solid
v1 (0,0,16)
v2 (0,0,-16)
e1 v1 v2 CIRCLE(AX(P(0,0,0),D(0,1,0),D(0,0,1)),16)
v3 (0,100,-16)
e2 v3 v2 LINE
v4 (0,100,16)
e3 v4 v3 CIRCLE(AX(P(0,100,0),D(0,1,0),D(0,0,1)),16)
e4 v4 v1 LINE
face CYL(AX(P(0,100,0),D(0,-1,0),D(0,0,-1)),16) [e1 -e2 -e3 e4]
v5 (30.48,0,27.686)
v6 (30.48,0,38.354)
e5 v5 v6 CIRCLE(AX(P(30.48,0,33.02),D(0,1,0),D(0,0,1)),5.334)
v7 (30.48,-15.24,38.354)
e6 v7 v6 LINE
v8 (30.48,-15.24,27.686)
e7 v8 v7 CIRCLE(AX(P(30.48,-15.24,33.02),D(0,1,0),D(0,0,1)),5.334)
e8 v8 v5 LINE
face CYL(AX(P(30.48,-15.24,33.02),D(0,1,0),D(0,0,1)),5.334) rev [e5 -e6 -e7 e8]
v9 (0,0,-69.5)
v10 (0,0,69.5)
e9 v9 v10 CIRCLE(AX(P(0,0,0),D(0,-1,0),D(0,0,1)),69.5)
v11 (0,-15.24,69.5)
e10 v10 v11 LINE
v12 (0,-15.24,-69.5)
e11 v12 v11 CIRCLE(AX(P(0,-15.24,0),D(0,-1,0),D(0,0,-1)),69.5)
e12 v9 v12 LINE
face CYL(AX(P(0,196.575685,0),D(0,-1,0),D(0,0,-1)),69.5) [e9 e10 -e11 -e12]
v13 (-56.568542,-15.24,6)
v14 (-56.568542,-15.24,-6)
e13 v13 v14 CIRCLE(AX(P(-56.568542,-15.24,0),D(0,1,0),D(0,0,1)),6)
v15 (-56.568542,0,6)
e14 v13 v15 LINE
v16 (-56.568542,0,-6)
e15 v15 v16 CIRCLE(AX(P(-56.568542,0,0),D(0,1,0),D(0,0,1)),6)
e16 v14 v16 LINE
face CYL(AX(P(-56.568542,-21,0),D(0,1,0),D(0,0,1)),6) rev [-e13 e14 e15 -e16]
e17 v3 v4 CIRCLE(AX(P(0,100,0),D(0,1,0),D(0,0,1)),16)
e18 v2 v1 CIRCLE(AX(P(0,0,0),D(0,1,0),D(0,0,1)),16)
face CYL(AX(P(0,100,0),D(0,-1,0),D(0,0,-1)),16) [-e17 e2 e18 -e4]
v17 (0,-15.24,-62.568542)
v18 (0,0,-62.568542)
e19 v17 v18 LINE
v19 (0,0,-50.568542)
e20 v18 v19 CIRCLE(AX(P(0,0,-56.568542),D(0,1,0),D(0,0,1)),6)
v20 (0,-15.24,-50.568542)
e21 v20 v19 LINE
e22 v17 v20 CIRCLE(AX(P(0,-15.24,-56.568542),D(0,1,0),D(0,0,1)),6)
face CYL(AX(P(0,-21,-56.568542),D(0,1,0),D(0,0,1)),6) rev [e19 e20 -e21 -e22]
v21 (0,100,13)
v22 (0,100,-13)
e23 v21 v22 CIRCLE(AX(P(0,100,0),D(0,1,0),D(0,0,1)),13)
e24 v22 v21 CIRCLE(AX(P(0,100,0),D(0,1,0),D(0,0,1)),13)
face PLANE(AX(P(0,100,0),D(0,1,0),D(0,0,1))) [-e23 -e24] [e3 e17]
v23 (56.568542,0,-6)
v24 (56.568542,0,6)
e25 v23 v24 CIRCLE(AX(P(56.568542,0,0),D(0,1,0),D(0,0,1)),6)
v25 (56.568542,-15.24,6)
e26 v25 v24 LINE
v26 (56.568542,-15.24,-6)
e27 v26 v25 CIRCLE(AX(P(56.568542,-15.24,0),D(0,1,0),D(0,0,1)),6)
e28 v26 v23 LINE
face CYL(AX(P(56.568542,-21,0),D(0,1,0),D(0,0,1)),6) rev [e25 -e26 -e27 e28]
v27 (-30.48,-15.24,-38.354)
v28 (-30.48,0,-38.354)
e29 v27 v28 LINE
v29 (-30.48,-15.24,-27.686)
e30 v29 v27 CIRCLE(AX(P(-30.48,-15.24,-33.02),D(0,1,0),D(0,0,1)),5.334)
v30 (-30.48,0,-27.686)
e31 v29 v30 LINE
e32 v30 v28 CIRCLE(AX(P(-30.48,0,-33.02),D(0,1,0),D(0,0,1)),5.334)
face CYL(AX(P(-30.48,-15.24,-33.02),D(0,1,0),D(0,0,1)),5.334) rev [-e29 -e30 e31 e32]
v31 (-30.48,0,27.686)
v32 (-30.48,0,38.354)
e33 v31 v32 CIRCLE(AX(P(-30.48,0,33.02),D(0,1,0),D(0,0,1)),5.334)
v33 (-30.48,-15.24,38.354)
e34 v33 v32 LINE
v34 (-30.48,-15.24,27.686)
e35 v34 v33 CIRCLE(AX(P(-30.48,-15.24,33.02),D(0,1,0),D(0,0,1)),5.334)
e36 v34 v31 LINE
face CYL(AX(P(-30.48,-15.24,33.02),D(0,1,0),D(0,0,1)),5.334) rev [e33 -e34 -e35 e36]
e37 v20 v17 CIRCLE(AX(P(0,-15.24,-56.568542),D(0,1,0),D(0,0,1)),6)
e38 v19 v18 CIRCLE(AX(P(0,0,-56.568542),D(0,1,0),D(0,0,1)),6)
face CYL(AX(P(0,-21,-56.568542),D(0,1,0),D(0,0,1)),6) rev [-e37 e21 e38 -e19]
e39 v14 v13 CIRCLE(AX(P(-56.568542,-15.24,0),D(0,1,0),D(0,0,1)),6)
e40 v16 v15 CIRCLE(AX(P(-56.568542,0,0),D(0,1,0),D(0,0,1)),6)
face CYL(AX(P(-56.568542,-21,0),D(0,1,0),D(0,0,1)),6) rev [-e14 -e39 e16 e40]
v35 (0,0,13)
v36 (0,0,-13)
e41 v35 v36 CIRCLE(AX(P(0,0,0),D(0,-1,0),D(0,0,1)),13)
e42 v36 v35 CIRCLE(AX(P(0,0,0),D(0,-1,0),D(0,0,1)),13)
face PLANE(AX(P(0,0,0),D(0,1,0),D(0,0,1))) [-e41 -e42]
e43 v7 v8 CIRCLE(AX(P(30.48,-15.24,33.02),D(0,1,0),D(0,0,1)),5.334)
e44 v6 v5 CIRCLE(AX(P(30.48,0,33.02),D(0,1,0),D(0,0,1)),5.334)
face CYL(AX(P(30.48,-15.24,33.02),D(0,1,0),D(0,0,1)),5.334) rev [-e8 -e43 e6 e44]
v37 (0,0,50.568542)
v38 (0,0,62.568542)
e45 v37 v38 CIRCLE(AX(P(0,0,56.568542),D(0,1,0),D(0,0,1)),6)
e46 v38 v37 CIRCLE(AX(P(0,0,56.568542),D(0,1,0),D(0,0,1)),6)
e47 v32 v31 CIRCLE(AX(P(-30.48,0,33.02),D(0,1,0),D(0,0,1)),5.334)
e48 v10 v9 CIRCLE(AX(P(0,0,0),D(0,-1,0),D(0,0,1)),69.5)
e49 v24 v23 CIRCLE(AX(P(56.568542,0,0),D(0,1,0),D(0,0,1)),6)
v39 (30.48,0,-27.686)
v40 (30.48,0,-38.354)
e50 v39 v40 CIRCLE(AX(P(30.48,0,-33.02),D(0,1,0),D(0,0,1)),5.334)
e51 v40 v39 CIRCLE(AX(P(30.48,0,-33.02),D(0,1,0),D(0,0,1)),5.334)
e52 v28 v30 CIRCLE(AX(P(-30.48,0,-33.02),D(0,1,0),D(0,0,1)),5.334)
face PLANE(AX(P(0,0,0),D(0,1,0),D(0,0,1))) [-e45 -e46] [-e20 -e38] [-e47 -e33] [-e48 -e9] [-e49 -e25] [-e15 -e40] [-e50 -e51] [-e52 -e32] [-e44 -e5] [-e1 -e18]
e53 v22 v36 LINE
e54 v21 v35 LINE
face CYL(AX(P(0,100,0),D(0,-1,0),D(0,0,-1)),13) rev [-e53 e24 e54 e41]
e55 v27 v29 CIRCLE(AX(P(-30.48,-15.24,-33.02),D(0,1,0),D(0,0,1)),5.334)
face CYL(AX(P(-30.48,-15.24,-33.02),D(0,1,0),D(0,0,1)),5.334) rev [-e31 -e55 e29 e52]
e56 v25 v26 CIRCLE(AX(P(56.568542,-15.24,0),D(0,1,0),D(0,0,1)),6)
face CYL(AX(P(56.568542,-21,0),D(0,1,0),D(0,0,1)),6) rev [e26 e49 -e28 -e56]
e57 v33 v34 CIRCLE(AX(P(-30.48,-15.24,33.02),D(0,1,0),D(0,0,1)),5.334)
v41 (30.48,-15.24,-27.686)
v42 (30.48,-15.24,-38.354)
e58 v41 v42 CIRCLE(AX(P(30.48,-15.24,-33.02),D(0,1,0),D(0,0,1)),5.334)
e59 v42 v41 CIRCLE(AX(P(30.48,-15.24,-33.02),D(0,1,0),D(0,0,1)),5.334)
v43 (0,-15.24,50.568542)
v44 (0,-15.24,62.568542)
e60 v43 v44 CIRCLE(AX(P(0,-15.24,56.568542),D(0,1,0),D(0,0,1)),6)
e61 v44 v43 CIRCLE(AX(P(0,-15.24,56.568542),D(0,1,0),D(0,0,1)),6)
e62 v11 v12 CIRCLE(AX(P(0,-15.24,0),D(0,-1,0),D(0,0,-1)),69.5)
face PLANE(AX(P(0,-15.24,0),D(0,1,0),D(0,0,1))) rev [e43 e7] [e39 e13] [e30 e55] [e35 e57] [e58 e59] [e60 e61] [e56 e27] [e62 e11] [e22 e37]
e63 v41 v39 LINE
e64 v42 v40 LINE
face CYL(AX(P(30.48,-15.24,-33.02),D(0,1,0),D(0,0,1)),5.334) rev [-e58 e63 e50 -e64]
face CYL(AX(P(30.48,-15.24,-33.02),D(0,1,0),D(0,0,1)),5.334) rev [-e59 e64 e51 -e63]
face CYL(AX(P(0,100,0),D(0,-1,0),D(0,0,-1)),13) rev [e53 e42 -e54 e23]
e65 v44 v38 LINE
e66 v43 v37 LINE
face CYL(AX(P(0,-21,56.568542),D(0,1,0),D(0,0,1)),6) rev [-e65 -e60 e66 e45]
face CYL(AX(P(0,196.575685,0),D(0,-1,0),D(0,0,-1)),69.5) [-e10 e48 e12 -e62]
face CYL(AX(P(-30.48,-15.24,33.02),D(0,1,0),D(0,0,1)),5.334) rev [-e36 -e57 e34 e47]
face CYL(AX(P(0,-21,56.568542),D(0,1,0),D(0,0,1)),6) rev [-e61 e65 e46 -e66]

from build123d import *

# Parameters (mm, degrees)
SKETCH1_R           = 31.75
SKETCH1_R_2         = 2.667
BOSS_EXTRUDE1_DEPTH = 7.62
SKETCH2_R           = 6.604
CUT_EXTRUDE1_DEPTH  = 46.543269536
SKETCH_1_R          = 7.5
EXTRUDE_1_DEPTH     = 7.62
SKETCH_2_R          = 8
SKETCH_2_R_2        = 6.5
BOSS_EXTRUDE2_DEPTH = 50
SCALE1_SCALE        = 2
SKETCH3_R           = 6
CUT_EXTRUDE_1_DEPTH = 21
BOSS_EXTRUDE3_START = -15.24
SKETCH5_R           = 69.5
SKETCH5_R_2         = 63.5
BOSS_EXTRUDE3_DEPTH = 15.24


with BuildPart() as part:
    # Sketch1 → Boss-Extrude1 (new body)
    with BuildSketch(Plane(origin=(0, 0, 0), x_dir=(1, 0, 0), z_dir=(0, 1, 0))):
        with Locations(Location((0, 0, 0), (0, 0, 270))):
            Circle(SKETCH1_R)
        with Locations(Location((-15.24, 16.51, 0), (0, 0, 270))):
            Circle(SKETCH1_R_2, mode=Mode.SUBTRACT)
        with Locations(Location((15.24, 16.51, 0), (0, 0, 270))):
            Circle(SKETCH1_R_2, mode=Mode.SUBTRACT)
        with Locations(Location((15.24, -16.51, 0), (0, 0, 270))):
            Circle(SKETCH1_R_2, mode=Mode.SUBTRACT)
        with Locations(Location((-15.24, -16.51, 0), (0, 0, 270))):
            Circle(SKETCH1_R_2, mode=Mode.SUBTRACT)
    extrude(amount=-BOSS_EXTRUDE1_DEPTH)

    # Sketch2 → Cut-Extrude1 (cut, through all)
    with BuildSketch(Plane(origin=(0, 0, 0), x_dir=(1, 0, 0), z_dir=(0, 1, 0))):
        with Locations(Location((0, 0, 0), (0, 0, 270))):
            Circle(SKETCH2_R)
    extrude(amount=-CUT_EXTRUDE1_DEPTH, mode=Mode.SUBTRACT)

    # 草图1 → 凸台-拉伸1 (add)
    with BuildSketch(Plane.XZ.offset(7.62)):
        Circle(SKETCH_1_R)
    extrude(amount=-EXTRUDE_1_DEPTH)

    # 草图2 → Boss-Extrude2 (add)
    with BuildSketch(Plane(origin=(0, 0, 0), x_dir=(1, 0, 0), z_dir=(0, 1, 0))):
        with Locations(Location((0, 0, 0), (0, 0, 270))):
            Circle(SKETCH_2_R)
        with Locations(Location((0, 0, 0), (0, 0, 270))):
            Circle(SKETCH_2_R_2, mode=Mode.SUBTRACT)
    extrude(amount=BOSS_EXTRUDE2_DEPTH)


with BuildPart() as part_1:
    # Scale1: scaled about (0, 0, 0)
    add(part.part.scale(SCALE1_SCALE))

    # Sketch3 → 切除-拉伸1 (cut)
    with BuildSketch(Plane(origin=(0, 0, 0), x_dir=(1, 0, 0), z_dir=(0, 1, 0))):
        with Locations(Location((56.568542495, 0, 0), (0, 0, 270))):
            Circle(SKETCH3_R)
        with Locations(Location((0, -56.568542495, 0), (0, 0, 270))):
            Circle(SKETCH3_R)
        with Locations(Location((-56.568542495, 0, 0), (0, 0, 270))):
            Circle(SKETCH3_R)
        with Locations(Location((0, 56.568542495, 0), (0, 0, 270))):
            Circle(SKETCH3_R)
    extrude(amount=-CUT_EXTRUDE_1_DEPTH, mode=Mode.SUBTRACT)

    # Sketch5 → Boss-Extrude3 (add)
    with BuildSketch(Plane.XZ.offset(15.24).offset(BOSS_EXTRUDE3_START)):
        with Locations(Location((0, 0, 0), (0, 0, 270))):
            Circle(SKETCH5_R)
        Circle(SKETCH5_R_2, mode=Mode.SUBTRACT)
    extrude(amount=BOSS_EXTRUDE3_DEPTH)


solid = part_1.part
